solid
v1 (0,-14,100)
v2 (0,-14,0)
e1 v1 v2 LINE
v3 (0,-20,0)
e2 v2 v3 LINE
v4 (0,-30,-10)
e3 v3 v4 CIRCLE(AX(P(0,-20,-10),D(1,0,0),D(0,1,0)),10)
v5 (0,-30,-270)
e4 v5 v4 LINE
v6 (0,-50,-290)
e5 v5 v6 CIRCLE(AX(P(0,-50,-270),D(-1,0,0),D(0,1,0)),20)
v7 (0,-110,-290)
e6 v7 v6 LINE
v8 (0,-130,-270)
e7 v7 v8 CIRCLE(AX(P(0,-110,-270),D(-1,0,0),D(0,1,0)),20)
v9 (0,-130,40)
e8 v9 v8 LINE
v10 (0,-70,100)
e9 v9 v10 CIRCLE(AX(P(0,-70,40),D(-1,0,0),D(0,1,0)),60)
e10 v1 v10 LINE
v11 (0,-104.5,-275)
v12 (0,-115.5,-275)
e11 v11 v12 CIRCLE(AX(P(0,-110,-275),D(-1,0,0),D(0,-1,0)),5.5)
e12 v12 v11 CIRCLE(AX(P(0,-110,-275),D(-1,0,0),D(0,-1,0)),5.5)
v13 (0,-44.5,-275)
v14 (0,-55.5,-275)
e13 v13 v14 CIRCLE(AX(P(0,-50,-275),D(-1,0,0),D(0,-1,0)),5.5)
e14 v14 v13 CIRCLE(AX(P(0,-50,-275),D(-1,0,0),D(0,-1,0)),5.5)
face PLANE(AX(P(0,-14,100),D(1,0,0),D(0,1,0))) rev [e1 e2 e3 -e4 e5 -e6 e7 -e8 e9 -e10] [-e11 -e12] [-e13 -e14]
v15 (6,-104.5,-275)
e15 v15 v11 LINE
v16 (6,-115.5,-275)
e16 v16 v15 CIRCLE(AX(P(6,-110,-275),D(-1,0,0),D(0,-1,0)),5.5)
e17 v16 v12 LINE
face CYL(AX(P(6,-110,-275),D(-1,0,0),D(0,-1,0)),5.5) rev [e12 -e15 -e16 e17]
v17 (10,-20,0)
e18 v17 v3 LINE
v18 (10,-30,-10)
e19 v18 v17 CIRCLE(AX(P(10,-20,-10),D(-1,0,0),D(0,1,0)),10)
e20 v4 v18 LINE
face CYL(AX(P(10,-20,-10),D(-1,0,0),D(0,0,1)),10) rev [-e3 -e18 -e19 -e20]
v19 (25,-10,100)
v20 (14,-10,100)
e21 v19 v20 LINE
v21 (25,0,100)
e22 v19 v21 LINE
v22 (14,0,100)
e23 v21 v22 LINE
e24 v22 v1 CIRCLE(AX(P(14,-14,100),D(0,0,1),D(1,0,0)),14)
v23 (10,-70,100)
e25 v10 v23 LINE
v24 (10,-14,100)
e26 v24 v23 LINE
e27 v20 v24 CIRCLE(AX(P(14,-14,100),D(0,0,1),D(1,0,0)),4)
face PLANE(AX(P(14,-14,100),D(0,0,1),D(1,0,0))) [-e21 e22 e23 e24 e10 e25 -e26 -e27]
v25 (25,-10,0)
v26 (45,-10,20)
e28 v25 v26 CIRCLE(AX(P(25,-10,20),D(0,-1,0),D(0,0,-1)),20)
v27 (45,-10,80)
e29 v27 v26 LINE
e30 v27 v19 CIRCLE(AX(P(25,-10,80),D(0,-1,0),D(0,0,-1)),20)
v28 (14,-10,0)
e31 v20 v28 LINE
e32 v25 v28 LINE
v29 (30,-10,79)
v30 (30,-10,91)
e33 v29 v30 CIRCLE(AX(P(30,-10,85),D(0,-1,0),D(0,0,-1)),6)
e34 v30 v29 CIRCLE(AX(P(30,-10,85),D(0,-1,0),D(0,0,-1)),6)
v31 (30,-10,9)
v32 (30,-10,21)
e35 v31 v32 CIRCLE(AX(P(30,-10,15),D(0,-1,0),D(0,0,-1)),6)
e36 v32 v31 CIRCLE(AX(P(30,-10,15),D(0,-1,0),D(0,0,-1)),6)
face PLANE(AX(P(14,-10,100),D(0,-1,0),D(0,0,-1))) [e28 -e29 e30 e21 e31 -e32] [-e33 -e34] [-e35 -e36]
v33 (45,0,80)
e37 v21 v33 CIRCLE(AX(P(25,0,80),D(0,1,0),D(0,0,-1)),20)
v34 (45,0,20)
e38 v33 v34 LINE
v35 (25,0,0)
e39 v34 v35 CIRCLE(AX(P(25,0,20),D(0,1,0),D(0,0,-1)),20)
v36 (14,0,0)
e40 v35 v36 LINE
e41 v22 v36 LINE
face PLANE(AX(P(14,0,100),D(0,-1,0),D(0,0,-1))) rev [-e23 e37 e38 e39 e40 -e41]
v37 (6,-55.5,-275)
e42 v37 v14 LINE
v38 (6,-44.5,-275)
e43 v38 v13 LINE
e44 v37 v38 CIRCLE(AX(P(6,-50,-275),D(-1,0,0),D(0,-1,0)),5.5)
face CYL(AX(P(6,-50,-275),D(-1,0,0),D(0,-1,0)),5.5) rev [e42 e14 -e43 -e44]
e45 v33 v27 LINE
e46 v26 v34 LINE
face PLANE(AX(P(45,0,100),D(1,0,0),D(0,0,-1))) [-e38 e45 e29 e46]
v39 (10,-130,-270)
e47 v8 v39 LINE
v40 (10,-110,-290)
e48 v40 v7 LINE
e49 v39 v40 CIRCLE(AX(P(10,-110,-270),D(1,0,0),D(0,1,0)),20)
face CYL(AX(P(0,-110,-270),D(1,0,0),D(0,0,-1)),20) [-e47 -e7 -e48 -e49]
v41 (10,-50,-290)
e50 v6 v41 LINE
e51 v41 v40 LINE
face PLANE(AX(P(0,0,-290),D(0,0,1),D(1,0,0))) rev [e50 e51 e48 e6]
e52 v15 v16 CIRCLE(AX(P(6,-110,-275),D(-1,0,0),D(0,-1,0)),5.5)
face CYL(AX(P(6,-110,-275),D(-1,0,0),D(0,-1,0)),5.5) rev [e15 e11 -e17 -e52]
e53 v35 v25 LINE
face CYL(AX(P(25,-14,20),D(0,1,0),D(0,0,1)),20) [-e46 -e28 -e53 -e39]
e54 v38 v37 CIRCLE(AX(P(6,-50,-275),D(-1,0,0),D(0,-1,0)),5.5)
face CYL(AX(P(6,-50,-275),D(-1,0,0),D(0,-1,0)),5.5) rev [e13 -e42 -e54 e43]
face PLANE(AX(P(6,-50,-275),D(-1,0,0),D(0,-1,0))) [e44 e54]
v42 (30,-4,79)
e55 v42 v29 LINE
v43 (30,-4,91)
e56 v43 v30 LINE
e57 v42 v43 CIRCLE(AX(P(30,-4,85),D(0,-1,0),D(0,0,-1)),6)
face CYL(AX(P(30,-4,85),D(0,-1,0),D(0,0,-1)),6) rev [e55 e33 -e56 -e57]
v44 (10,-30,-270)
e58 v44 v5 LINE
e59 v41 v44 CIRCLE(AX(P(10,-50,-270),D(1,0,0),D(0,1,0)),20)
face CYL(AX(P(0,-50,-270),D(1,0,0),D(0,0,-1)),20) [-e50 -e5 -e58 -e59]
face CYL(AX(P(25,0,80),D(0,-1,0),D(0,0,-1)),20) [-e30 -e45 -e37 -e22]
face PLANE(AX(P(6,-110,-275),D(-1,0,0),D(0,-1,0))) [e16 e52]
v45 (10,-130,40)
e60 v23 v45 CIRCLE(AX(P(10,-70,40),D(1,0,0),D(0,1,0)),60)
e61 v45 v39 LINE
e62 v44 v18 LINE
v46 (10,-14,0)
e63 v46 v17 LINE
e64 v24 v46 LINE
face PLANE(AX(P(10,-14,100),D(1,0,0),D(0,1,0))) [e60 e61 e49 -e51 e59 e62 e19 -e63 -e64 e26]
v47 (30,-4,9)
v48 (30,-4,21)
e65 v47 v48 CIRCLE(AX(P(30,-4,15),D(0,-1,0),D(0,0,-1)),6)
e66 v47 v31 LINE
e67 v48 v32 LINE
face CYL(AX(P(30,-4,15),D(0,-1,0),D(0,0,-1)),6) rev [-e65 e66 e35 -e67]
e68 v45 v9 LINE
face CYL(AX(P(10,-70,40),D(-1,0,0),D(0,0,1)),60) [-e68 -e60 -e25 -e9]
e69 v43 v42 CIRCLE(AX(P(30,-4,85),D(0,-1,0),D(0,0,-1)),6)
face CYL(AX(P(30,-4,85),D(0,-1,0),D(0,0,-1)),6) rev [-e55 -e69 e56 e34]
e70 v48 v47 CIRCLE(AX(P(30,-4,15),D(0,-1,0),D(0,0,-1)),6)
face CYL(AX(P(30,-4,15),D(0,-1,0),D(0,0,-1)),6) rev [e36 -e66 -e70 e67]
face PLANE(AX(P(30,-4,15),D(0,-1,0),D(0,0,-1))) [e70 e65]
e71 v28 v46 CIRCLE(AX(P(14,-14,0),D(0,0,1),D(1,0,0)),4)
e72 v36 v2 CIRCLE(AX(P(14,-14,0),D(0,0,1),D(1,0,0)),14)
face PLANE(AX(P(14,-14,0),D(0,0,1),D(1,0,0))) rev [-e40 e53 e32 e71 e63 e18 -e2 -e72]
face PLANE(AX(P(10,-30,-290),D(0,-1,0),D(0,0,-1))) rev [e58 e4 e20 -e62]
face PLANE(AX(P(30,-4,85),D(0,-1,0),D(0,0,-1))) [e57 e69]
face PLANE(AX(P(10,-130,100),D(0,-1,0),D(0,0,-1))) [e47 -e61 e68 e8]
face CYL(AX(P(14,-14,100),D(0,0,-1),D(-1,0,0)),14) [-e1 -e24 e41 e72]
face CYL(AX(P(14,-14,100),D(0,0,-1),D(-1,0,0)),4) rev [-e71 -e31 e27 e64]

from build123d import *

# Parameters (mm, degrees)
EXTRUDE_THIN1_DEPTH = 100
SKETCH2_W           = 10
SKETCH2_H           = 100
BOSS_EXTRUDE1_DEPTH = 290
FILLET1_R           = 60
FILLET2_R           = 20
FILLET3_R           = 10
SKETCH3_R           = 6
CUT_EXTRUDE1_DEPTH  = 6
LPATTERN1_COUNT     = 2
LPATTERN1_PITCH     = 70
SKETCH4_R           = 5.5
CUT_EXTRUDE2_DEPTH  = 6
LPATTERN2_COUNT     = 2
LPATTERN2_PITCH     = 60


with BuildPart() as part:
    # Sketch1 → Extrude-Thin1 (new body)
    with BuildSketch(Plane.XY):
        with BuildLine():
            Line((0, -130), (0, -14))
            ThreePointArc((0, -14), (4.100505063, -4.100505063), (14, 0))
            Line((14, 0), (45, 0))
            Line((45, 0), (45, -10))
            Line((45, -10), (14, -10))
            ThreePointArc((14, -10), (11.171572875, -11.171572875), (10, -14))
            Line((10, -14), (10, -130))
            Line((10, -130), (0, -130))
        make_face()
    extrude(amount=EXTRUDE_THIN1_DEPTH)

    # Sketch2 → Boss-Extrude1 (add)
    with BuildSketch(Plane(origin=(0, 0, 0), x_dir=(-1, 0, 0), z_dir=(0, 0, -1))):
        with Locations((-5, -80)):
            Rectangle(SKETCH2_W, SKETCH2_H)
    extrude(amount=BOSS_EXTRUDE1_DEPTH)

    # Fillet1
    fillet1_edges = [part.edges().sort_by_distance(p)[0] for p in [
        (5, -130, 100),
    ]]
    fillet(fillet1_edges, radius=FILLET1_R)

    # Fillet2
    fillet2_edges = [part.edges().sort_by_distance(p)[0] for p in [
        (5, -30, -290),
        (5, -130, -290),
        (45, -5, 0),
        (45, -5, 100),
    ]]
    fillet(fillet2_edges, radius=FILLET2_R)

    # Fillet3
    fillet3_edges = [part.edges().sort_by_distance(p)[0] for p in [
        (5, -30, 0),
    ]]
    fillet(fillet3_edges, radius=FILLET3_R)

    # Sketch3 → Cut-Extrude1 (cut)
    with BuildSketch(Plane.XZ.offset(10)):
        with Locations(Location((30, 85, 0), (0, 0, 270))):
            Circle(SKETCH3_R)
    cut_extrude1 = extrude(amount=-CUT_EXTRUDE1_DEPTH, mode=Mode.SUBTRACT)

    # LPattern1: Cut-Extrude1 ×2
    with Locations(*[(0, 0, -i * LPATTERN1_PITCH) for i in range(1, LPATTERN1_COUNT)]):
        add(cut_extrude1, mode=Mode.SUBTRACT)

    # Sketch4 → Cut-Extrude2 (cut)
    with BuildSketch(Plane.ZY):
        with Locations(Location((-275, -50, 0), (0, 0, 270))):
            Circle(SKETCH4_R)
    cut_extrude2 = extrude(amount=-CUT_EXTRUDE2_DEPTH, mode=Mode.SUBTRACT)

    # LPattern2: Cut-Extrude2 ×2
    with Locations(*[(0, -i * LPATTERN2_PITCH, 0) for i in range(1, LPATTERN2_COUNT)]):
        add(cut_extrude2, mode=Mode.SUBTRACT)


solid = part.part
